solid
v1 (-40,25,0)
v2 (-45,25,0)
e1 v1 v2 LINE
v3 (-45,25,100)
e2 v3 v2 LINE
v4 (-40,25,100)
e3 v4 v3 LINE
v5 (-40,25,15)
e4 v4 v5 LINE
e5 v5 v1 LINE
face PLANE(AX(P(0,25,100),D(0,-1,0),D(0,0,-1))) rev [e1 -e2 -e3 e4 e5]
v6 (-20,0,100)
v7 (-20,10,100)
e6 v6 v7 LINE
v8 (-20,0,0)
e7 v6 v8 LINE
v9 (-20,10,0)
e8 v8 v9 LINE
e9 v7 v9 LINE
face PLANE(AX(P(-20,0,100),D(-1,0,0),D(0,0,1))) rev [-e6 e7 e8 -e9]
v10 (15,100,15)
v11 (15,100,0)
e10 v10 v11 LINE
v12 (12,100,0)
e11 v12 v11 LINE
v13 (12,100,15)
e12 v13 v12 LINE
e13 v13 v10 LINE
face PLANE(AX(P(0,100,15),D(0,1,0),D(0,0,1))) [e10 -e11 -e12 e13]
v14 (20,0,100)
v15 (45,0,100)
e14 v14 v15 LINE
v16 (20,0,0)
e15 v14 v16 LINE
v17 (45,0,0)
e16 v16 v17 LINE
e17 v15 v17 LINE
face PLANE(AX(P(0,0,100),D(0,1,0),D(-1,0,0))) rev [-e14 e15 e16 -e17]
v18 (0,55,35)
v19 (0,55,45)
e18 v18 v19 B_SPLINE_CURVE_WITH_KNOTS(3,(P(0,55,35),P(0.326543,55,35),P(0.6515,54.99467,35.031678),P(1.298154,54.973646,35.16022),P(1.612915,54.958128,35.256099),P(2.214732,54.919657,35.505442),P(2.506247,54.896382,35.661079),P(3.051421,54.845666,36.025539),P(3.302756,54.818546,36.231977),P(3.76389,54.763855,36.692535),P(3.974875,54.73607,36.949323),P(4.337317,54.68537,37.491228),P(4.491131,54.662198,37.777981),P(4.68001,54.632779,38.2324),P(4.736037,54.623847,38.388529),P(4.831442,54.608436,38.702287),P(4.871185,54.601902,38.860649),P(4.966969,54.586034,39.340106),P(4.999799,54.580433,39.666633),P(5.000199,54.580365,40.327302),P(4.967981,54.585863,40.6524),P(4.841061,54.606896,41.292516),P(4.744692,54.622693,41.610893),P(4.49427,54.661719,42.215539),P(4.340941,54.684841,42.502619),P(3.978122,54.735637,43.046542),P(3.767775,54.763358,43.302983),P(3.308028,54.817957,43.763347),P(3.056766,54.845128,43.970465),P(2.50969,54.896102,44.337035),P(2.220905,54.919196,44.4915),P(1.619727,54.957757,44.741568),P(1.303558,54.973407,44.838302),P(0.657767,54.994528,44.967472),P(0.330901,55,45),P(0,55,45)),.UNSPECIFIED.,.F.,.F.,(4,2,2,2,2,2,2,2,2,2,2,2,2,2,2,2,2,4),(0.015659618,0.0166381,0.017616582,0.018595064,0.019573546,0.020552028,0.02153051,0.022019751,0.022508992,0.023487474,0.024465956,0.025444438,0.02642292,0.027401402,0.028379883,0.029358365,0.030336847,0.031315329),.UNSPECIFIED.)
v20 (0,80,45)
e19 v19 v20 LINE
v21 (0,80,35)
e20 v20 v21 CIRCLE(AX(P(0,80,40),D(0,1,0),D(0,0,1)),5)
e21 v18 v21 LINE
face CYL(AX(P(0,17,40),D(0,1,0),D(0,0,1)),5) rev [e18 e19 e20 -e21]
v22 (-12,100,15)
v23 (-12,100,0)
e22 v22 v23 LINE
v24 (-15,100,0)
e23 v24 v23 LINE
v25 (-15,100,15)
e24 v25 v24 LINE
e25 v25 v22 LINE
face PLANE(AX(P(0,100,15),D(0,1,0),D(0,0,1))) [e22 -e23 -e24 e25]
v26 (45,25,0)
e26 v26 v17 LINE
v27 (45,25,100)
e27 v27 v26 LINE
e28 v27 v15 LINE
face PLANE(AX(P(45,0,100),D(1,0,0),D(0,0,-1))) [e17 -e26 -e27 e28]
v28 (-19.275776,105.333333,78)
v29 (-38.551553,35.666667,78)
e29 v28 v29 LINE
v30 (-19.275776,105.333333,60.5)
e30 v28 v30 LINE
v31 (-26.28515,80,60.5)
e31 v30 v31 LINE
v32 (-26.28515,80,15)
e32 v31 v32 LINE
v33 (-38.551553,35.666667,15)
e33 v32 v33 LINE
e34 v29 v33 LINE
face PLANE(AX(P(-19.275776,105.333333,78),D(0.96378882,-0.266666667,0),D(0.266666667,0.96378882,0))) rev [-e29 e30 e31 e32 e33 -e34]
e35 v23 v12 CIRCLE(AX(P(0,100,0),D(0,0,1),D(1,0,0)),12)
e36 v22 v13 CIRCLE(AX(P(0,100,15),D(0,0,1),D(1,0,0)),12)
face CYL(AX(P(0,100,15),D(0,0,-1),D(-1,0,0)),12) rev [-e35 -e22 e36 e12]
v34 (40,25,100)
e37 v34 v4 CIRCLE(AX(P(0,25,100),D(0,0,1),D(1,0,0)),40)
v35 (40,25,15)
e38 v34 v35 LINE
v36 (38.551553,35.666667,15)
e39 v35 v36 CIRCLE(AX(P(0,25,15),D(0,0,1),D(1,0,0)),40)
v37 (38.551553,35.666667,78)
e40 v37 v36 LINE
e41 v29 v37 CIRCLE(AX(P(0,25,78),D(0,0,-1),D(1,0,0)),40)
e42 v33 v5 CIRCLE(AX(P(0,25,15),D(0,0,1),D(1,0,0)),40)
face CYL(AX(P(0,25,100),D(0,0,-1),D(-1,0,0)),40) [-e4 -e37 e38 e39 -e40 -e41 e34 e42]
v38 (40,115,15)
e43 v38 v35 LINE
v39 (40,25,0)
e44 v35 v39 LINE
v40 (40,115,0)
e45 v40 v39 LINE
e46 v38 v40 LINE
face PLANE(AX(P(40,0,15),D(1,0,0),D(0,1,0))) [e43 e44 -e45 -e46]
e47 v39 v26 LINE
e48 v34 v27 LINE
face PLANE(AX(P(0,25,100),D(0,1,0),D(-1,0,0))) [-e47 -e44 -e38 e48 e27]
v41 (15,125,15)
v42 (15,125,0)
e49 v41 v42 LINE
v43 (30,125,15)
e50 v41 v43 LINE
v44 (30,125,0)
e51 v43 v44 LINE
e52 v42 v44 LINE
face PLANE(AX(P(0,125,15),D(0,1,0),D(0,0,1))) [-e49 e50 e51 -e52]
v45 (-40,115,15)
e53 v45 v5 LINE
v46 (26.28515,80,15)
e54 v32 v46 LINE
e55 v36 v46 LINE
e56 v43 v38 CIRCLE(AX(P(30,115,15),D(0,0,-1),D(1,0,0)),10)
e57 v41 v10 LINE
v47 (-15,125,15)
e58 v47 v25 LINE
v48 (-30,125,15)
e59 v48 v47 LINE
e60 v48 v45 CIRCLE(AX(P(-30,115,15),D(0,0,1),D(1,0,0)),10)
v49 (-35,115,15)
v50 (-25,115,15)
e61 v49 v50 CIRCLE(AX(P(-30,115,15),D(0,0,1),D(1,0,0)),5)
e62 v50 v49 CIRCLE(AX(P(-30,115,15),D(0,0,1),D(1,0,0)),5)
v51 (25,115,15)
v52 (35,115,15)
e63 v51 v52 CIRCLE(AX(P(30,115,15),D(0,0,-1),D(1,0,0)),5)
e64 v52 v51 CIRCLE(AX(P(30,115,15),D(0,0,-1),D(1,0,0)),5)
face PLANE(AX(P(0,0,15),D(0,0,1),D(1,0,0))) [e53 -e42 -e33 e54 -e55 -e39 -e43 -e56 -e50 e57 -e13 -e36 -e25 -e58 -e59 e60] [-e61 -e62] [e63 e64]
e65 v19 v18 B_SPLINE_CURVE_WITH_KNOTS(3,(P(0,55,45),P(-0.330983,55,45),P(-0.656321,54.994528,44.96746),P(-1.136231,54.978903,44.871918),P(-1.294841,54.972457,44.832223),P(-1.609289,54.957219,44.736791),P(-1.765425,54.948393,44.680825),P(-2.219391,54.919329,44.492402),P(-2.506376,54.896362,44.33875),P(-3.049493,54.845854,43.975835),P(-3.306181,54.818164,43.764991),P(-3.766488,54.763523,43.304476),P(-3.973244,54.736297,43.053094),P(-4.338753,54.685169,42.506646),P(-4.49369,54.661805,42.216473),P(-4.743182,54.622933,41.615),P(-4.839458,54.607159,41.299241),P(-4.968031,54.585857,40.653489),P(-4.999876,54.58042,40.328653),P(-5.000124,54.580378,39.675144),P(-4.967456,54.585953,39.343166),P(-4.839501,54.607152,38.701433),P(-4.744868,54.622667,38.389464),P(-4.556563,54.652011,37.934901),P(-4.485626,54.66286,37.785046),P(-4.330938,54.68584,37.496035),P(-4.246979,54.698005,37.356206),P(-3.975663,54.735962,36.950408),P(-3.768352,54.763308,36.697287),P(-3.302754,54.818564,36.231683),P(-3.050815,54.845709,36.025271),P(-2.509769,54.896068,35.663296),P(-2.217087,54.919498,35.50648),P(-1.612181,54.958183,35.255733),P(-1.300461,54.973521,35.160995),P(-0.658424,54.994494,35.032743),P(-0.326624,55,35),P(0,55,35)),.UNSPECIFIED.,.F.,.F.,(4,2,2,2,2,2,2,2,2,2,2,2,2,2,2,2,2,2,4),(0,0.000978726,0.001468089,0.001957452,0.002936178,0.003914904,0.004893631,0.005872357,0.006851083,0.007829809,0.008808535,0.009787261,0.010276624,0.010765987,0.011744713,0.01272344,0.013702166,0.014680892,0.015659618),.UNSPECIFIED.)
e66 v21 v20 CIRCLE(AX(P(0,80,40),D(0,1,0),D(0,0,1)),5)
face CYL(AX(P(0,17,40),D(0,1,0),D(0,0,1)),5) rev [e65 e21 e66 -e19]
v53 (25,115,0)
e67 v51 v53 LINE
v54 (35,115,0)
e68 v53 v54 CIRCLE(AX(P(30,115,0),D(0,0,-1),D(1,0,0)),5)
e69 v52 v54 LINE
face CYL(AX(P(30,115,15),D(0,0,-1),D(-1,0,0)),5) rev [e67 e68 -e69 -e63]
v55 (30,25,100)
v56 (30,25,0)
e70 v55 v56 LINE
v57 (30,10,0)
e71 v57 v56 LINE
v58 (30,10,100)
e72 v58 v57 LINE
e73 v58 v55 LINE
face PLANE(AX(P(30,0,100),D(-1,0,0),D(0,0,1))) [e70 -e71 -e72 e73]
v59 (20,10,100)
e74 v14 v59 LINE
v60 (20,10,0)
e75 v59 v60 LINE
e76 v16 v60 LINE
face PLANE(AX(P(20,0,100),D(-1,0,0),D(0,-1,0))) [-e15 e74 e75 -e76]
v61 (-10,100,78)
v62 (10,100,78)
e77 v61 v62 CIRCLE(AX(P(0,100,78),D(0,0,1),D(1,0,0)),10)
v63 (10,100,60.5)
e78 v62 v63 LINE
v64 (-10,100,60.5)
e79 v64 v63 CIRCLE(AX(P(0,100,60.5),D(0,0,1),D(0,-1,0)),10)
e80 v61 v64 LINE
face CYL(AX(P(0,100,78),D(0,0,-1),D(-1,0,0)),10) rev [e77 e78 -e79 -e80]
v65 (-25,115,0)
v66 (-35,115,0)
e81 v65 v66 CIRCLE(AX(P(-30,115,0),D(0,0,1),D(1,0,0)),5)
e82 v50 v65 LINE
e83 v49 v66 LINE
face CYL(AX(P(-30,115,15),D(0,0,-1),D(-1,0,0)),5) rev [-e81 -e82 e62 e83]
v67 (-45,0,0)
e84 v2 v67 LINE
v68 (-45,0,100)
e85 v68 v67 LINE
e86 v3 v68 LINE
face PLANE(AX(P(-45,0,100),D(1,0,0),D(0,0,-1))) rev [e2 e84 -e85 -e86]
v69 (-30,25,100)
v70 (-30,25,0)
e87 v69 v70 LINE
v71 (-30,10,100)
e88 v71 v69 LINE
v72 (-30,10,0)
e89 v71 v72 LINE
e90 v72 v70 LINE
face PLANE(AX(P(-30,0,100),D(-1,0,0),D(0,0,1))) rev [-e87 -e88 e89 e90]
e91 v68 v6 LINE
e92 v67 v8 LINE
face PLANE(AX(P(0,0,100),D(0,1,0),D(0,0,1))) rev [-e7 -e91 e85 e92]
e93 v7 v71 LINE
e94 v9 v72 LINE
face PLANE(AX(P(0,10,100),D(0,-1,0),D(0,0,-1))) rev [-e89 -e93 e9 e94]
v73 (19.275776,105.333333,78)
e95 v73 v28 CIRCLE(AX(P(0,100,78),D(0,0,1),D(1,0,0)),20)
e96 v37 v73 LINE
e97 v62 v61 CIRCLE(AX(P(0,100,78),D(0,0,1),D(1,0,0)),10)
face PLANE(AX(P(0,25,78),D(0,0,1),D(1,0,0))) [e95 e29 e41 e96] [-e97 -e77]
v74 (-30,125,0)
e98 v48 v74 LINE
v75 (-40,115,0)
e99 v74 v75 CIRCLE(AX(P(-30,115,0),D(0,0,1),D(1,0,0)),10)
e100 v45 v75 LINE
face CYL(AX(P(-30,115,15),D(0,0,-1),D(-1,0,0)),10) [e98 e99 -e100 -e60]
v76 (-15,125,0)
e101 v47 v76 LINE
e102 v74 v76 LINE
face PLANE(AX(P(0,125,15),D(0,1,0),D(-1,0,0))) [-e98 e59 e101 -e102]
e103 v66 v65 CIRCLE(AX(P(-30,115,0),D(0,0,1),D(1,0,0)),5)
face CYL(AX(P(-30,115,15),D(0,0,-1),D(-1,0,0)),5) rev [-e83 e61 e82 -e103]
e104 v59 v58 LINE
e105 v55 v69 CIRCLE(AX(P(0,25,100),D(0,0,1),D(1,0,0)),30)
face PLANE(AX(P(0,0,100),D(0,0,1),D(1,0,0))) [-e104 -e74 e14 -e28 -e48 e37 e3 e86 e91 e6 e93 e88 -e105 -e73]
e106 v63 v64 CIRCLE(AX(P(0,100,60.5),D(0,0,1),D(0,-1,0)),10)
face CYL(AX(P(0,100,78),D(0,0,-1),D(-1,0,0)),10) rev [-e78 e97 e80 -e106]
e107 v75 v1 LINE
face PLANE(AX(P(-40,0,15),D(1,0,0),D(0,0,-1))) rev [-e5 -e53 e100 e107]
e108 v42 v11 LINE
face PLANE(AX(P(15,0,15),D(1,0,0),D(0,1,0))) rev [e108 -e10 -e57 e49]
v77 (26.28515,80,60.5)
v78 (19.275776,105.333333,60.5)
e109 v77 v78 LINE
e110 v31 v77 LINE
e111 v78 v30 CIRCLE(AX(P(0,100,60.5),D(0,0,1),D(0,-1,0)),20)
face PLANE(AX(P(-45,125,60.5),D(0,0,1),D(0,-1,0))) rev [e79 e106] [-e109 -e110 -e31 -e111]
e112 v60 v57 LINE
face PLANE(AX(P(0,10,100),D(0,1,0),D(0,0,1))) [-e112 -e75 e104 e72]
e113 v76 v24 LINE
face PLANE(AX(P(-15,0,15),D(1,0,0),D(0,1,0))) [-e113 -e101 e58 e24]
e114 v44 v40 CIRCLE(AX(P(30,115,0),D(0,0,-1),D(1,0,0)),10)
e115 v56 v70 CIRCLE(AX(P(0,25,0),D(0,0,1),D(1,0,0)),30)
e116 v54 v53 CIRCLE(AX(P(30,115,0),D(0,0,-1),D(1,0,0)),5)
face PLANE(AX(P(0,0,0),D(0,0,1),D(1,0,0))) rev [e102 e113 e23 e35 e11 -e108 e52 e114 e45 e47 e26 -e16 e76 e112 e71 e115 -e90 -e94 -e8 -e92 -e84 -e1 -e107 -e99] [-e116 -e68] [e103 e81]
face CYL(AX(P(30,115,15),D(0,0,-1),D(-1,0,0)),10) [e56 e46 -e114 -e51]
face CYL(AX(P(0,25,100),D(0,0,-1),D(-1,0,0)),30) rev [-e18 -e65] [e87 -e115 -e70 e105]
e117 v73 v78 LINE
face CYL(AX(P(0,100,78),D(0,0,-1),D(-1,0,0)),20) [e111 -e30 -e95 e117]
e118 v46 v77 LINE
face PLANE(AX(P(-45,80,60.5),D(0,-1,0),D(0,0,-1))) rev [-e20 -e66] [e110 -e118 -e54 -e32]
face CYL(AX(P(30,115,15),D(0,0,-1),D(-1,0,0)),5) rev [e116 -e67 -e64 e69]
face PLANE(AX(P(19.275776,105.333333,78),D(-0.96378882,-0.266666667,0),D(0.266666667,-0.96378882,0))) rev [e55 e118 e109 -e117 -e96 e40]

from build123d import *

# Parameters (mm, degrees)
FLANGE_PROFILE_SKETCH_R  = 5
FLANGE_PLATE_15MM_DEPTH  = 15
SADDLE_BODY_100MM_DEPTH  = 100
SUPPORT_BLOCK_SKETCH_R   = 10
SUPPORT_BLOCK_63MM_DEPTH = 63
SLOT_CUT_DEPTH           = 167.282891483
SLOT_CUT_DEPTH_BACK      = 167.282891483
SLOT_CUT_SKETCH_W        = 45.5
SLOT_CUT_SKETCH_H        = 45
CROSS_HOLE_SKETCH_R      = 5
CROSS_HOLE_DEPTH         = 63


with BuildPart() as part:
    # Flange Profile Sketch → Flange Plate 15mm (new body)
    with BuildSketch(Plane.XY):
        with BuildLine():
            ThreePointArc((-12, 100), (0, 88), (12, 100))
            Line((12, 100), (15, 100))
            Line((15, 100), (15, 125))
            Line((15, 125), (30, 125))
            ThreePointArc((30, 125), (37.071067812, 122.071067812), (40, 115))
            Line((40, 115), (40, 25))
            ThreePointArc((40, 25), (0, 65), (-40, 25))
            Line((-40, 25), (-40, 115))
            ThreePointArc((-40, 115), (-37.071067812, 122.071067812), (-30, 125))
            Line((-30, 125), (-15, 125))
            Line((-15, 125), (-15, 100))
            Line((-15, 100), (-12, 100))
        make_face()
        with Locations((-30, 115)):
            Circle(FLANGE_PROFILE_SKETCH_R, mode=Mode.SUBTRACT)
        with Locations((30, 115)):
            Circle(FLANGE_PROFILE_SKETCH_R, mode=Mode.SUBTRACT)
    extrude(amount=FLANGE_PLATE_15MM_DEPTH)

    # Sketch1_4 → Saddle Body 100mm (add)
    with BuildSketch(Plane.XY):
        with BuildLine():
            ThreePointArc((30, 25), (0, 55), (-30, 25))
            Line((-30, 25), (-30, 10))
            Line((-30, 10), (-20, 10))
            Line((-20, 10), (-20, 0))
            Line((-20, 0), (-45, 0))
            Line((-45, 0), (-45, 25))
            Line((-45, 25), (-40, 25))
            ThreePointArc((-40, 25), (0, 65), (40, 25))
            Line((40, 25), (45, 25))
            Line((45, 25), (45, 0))
            Line((45, 0), (20, 0))
            Line((20, 0), (20, 10))
            Line((20, 10), (30, 10))
            Line((30, 10), (30, 25))
        make_face()
    extrude(amount=SADDLE_BODY_100MM_DEPTH)

    # Support Block Sketch → Support Block 63mm (add)
    with BuildSketch(Plane.XY.offset(15)):
        with BuildLine():
            Line((-19.275776393, 105.333333333), (-38.551552786, 35.666666667))
            ThreePointArc((-38.551552786, 35.666666667), (0, 65), (38.551552786, 35.666666667))
            Line((38.551552786, 35.666666667), (19.275776393, 105.333333333))
            ThreePointArc((19.275776393, 105.333333333), (0, 120), (-19.275776393, 105.333333333))
        make_face()
        with Locations((0, 100)):
            Circle(SUPPORT_BLOCK_SKETCH_R, mode=Mode.SUBTRACT)
    extrude(amount=SUPPORT_BLOCK_63MM_DEPTH)

    # Slot Cut Sketch → Slot Cut (cut, two sides: drawn at the far end of the back side and taken through both)
    with BuildSketch(Plane(origin=(0, 0, 0), x_dir=(0, 0, -1), z_dir=(1, 0, 0)).offset(-SLOT_CUT_DEPTH_BACK)):
        with Locations((-37.75, 102.5)):
            Rectangle(SLOT_CUT_SKETCH_W, SLOT_CUT_SKETCH_H)
    extrude(amount=SLOT_CUT_DEPTH + SLOT_CUT_DEPTH_BACK, mode=Mode.SUBTRACT)

    # Cross Hole Sketch → Cross Hole (cut)
    with BuildSketch(Plane(origin=(0, 80, 0), x_dir=(1, 0, 0), z_dir=(0, 1, 0))):
        with Locations(Location((0, -40, 0), (0, 0, 270))):
            Circle(CROSS_HOLE_SKETCH_R)
    extrude(amount=-CROSS_HOLE_DEPTH, mode=Mode.SUBTRACT)


solid = part.part
